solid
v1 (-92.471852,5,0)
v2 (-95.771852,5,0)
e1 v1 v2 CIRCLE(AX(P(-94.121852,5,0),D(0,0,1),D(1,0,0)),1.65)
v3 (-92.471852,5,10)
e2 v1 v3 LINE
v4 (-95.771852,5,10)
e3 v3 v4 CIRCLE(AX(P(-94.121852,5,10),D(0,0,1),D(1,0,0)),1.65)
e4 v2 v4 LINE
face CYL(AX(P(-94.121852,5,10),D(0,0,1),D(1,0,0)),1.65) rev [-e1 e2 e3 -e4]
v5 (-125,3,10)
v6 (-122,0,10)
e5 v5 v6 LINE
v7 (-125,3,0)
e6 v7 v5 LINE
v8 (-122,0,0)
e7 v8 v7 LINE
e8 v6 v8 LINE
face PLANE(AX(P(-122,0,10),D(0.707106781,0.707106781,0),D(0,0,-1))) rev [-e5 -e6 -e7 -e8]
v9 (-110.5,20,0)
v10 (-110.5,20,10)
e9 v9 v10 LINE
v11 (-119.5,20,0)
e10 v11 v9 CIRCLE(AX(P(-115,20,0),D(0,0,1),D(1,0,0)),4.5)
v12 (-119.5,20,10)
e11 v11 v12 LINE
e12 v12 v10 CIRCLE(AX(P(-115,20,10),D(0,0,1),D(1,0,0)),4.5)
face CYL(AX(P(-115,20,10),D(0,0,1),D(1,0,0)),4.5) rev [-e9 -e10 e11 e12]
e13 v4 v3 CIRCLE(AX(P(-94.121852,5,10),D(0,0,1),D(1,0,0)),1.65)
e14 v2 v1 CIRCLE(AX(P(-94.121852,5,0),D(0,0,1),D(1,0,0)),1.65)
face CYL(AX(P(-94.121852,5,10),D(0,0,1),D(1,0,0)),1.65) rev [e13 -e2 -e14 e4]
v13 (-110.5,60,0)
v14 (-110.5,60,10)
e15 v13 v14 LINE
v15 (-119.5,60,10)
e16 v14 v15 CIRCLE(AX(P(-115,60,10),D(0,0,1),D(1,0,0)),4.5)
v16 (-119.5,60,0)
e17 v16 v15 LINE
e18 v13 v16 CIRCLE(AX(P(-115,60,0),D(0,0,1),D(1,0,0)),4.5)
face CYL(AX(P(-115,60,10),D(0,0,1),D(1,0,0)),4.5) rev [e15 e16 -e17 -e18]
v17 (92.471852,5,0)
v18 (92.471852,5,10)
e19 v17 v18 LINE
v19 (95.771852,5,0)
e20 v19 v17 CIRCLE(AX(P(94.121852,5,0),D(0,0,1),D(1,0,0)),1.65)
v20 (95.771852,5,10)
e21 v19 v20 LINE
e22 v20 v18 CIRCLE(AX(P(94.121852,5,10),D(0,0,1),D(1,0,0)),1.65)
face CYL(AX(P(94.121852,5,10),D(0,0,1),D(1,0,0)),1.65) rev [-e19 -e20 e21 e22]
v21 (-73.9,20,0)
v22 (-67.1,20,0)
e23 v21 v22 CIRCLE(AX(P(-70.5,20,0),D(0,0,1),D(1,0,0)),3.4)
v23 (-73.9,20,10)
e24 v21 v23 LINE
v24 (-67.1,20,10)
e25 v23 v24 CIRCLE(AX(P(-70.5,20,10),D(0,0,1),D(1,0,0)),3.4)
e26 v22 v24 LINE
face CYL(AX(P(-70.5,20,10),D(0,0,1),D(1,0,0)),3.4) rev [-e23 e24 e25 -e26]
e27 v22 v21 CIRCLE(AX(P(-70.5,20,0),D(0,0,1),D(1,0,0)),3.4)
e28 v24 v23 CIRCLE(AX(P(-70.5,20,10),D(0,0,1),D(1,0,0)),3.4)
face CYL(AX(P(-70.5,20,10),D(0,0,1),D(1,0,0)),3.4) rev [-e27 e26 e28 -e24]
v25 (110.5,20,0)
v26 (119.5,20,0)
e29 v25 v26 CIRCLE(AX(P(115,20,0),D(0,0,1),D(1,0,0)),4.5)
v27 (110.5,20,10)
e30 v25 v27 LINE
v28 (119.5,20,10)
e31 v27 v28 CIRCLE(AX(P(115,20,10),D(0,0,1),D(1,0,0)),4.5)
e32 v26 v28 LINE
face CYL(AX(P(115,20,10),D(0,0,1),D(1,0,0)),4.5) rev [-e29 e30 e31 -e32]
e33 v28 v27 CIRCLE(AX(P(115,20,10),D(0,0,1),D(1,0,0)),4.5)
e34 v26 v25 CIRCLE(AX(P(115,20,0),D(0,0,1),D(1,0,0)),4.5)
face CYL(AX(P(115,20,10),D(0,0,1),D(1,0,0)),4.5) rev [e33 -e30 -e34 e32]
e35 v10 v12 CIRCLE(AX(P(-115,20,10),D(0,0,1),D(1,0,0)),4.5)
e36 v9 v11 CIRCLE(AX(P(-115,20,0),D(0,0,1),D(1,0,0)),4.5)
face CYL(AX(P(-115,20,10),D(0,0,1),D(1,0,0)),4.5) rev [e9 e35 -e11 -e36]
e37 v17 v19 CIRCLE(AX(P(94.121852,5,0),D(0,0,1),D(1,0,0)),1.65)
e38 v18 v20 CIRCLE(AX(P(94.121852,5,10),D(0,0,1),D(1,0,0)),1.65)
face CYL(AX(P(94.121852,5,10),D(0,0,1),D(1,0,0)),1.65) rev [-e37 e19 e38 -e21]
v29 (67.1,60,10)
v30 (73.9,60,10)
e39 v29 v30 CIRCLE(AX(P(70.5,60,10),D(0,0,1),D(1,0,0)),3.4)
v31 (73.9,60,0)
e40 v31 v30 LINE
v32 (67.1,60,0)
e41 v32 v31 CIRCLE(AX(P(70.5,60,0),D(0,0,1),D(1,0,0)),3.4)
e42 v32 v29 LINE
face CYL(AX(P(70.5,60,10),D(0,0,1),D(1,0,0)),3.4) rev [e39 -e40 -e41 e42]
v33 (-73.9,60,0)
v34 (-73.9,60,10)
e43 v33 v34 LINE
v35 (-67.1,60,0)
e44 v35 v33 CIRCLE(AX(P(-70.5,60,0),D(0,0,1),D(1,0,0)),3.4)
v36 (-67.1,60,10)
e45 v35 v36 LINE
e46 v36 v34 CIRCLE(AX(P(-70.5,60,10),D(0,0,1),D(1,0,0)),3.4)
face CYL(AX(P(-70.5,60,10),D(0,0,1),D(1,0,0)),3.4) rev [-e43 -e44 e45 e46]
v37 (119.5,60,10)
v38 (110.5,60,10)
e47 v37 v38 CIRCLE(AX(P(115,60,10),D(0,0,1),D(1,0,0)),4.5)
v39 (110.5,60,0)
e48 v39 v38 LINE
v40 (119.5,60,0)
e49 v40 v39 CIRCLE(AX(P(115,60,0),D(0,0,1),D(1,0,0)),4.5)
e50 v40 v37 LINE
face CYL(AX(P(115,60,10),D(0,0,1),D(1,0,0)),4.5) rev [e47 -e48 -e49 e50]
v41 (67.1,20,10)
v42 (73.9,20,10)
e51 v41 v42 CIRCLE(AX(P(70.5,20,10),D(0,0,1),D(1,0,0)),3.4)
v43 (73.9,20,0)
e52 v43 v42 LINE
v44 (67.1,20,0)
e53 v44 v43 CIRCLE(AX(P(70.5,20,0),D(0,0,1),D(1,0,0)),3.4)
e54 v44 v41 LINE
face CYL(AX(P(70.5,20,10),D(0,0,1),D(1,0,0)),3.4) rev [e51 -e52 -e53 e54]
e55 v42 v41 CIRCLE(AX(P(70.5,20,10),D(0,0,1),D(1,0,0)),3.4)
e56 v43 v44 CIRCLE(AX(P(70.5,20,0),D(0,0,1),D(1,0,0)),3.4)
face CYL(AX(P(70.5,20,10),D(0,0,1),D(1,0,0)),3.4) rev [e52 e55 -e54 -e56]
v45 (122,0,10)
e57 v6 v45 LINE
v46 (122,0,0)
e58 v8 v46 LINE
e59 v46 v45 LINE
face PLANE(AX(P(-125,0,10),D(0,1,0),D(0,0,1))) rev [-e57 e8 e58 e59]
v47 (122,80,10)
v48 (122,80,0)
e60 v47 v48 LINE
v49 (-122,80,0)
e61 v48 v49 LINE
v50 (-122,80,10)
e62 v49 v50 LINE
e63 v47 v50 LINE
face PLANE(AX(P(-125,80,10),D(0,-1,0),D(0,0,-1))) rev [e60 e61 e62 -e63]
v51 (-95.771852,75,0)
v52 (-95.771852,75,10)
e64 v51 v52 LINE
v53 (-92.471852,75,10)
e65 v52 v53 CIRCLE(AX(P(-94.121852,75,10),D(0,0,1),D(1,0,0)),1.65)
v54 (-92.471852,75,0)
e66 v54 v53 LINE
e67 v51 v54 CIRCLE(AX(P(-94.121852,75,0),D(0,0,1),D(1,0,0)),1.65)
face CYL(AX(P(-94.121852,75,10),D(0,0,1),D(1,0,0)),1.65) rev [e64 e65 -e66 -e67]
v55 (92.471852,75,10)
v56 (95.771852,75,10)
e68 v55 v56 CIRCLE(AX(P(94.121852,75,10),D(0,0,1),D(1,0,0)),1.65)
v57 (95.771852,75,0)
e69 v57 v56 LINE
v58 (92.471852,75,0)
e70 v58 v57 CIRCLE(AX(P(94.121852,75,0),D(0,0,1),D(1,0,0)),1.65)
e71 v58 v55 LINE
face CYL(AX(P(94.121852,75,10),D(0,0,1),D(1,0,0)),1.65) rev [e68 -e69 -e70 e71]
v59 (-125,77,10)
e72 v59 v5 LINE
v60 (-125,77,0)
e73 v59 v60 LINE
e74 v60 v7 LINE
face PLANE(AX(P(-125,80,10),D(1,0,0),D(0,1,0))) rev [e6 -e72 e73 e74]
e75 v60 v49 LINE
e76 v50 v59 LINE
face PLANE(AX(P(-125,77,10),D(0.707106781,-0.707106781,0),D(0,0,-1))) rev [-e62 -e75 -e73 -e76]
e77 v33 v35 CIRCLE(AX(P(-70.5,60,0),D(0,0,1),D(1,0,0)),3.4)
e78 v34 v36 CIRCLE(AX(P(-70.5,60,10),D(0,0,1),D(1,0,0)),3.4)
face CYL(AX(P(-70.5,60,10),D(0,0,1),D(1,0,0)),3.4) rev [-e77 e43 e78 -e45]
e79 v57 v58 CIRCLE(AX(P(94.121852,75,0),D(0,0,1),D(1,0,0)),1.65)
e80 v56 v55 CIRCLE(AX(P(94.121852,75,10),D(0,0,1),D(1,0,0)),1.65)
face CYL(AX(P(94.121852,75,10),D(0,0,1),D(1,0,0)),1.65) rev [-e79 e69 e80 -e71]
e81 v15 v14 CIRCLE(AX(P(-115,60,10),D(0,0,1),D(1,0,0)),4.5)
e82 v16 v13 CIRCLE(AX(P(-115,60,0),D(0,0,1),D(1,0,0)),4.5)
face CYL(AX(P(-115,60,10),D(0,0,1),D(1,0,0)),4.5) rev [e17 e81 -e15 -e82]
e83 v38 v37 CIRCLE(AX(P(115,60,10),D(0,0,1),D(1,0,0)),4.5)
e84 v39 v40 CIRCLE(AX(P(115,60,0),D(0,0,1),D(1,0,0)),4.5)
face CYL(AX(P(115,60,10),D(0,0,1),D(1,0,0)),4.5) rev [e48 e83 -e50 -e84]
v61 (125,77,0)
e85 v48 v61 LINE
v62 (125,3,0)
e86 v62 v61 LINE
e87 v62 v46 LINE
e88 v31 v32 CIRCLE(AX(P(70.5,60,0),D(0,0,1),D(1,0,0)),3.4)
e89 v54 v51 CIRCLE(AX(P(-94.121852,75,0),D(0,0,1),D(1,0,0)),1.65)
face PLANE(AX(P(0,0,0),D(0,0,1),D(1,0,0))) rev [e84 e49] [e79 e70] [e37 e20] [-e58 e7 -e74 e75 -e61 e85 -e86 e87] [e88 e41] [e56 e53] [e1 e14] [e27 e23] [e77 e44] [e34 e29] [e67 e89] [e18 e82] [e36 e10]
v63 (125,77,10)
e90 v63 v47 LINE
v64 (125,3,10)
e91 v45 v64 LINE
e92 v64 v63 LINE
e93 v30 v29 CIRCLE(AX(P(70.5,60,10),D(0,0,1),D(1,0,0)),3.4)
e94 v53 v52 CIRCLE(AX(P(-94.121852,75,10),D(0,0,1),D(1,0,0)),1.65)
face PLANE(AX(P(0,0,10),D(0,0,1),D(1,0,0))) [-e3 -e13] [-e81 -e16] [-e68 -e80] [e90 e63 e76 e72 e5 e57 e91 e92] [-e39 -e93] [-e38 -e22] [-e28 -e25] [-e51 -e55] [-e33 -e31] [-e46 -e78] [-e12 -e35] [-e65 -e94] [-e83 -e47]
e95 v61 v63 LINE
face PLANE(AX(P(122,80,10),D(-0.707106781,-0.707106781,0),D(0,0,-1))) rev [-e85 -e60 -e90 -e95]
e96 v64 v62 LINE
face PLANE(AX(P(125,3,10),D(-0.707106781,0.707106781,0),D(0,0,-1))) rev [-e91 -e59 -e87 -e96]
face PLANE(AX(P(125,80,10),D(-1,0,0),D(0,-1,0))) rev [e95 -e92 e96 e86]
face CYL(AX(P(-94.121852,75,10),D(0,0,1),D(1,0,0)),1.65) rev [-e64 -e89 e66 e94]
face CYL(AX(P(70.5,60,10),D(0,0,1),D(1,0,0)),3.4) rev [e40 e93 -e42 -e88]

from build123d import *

# Parameters (mm, degrees)
SKETCH_1_W            = 250
SKETCH_1_H            = 80
EXTRUDE_1_DEPTH       = 10
HOLE_WIZARD_9_0_9_1_D = 9
CHAMFER_1_SIZE        = 3
HOLE_WIZARD_M8_1_D    = 6.8
HOLE_WIZARD_M4_1_D    = 3.3


with BuildPart() as part:
    # 草图1 → 凸台-拉伸1 (new body)
    with BuildSketch(Plane.XY):
        with Locations((0, 40)):
            Rectangle(SKETCH_1_W, SKETCH_1_H)
    extrude(amount=EXTRUDE_1_DEPTH)

    # Ø9.0 (9) 直径孔1 (through all)
    with Locations(Plane.XY.offset(10)):
        with Locations((115, 20), (115, 60)):
            hole_wizard_9_0_9_1 = Hole(HOLE_WIZARD_9_0_9_1_D / 2)

    # 镜向1: Ø9.0 (9) 直径孔1 across plane
    add(hole_wizard_9_0_9_1.mirror(Plane(origin=(0, 0, 0), x_dir=(0, 0, 1), z_dir=(1, 0, 0))), mode=Mode.SUBTRACT)

    # 倒角1
    chamfer_1_edges = [part.edges().sort_by_distance(p)[0] for p in [
        (-125, 80, 5),
        (125, 80, 5),
        (125, 0, 5),
        (-125, 0, 5),
    ]]
    chamfer(chamfer_1_edges, length=CHAMFER_1_SIZE)

    # M8 螺纹孔1 (through all)
    with Locations(Plane.XY.offset(10)):
        with Locations((70.5, 60), (70.5, 20)):
            hole_wizard_m8_1 = Hole(HOLE_WIZARD_M8_1_D / 2)

    # 镜向2: M8 螺纹孔1 across plane
    add(hole_wizard_m8_1.mirror(Plane(origin=(0, 0, 0), x_dir=(0, 0, 1), z_dir=(1, 0, 0))), mode=Mode.SUBTRACT)

    # M4 螺纹孔1 (through all)
    with Locations(Plane.XY.offset(10)):
        with Locations((-94.121851999, 75), (-94.121851999, 5)):
            hole_wizard_m4_1 = Hole(HOLE_WIZARD_M4_1_D / 2)

    # 镜向3: M4 螺纹孔1 across plane
    add(hole_wizard_m4_1.mirror(Plane.ZY), mode=Mode.SUBTRACT)


solid = part.part
